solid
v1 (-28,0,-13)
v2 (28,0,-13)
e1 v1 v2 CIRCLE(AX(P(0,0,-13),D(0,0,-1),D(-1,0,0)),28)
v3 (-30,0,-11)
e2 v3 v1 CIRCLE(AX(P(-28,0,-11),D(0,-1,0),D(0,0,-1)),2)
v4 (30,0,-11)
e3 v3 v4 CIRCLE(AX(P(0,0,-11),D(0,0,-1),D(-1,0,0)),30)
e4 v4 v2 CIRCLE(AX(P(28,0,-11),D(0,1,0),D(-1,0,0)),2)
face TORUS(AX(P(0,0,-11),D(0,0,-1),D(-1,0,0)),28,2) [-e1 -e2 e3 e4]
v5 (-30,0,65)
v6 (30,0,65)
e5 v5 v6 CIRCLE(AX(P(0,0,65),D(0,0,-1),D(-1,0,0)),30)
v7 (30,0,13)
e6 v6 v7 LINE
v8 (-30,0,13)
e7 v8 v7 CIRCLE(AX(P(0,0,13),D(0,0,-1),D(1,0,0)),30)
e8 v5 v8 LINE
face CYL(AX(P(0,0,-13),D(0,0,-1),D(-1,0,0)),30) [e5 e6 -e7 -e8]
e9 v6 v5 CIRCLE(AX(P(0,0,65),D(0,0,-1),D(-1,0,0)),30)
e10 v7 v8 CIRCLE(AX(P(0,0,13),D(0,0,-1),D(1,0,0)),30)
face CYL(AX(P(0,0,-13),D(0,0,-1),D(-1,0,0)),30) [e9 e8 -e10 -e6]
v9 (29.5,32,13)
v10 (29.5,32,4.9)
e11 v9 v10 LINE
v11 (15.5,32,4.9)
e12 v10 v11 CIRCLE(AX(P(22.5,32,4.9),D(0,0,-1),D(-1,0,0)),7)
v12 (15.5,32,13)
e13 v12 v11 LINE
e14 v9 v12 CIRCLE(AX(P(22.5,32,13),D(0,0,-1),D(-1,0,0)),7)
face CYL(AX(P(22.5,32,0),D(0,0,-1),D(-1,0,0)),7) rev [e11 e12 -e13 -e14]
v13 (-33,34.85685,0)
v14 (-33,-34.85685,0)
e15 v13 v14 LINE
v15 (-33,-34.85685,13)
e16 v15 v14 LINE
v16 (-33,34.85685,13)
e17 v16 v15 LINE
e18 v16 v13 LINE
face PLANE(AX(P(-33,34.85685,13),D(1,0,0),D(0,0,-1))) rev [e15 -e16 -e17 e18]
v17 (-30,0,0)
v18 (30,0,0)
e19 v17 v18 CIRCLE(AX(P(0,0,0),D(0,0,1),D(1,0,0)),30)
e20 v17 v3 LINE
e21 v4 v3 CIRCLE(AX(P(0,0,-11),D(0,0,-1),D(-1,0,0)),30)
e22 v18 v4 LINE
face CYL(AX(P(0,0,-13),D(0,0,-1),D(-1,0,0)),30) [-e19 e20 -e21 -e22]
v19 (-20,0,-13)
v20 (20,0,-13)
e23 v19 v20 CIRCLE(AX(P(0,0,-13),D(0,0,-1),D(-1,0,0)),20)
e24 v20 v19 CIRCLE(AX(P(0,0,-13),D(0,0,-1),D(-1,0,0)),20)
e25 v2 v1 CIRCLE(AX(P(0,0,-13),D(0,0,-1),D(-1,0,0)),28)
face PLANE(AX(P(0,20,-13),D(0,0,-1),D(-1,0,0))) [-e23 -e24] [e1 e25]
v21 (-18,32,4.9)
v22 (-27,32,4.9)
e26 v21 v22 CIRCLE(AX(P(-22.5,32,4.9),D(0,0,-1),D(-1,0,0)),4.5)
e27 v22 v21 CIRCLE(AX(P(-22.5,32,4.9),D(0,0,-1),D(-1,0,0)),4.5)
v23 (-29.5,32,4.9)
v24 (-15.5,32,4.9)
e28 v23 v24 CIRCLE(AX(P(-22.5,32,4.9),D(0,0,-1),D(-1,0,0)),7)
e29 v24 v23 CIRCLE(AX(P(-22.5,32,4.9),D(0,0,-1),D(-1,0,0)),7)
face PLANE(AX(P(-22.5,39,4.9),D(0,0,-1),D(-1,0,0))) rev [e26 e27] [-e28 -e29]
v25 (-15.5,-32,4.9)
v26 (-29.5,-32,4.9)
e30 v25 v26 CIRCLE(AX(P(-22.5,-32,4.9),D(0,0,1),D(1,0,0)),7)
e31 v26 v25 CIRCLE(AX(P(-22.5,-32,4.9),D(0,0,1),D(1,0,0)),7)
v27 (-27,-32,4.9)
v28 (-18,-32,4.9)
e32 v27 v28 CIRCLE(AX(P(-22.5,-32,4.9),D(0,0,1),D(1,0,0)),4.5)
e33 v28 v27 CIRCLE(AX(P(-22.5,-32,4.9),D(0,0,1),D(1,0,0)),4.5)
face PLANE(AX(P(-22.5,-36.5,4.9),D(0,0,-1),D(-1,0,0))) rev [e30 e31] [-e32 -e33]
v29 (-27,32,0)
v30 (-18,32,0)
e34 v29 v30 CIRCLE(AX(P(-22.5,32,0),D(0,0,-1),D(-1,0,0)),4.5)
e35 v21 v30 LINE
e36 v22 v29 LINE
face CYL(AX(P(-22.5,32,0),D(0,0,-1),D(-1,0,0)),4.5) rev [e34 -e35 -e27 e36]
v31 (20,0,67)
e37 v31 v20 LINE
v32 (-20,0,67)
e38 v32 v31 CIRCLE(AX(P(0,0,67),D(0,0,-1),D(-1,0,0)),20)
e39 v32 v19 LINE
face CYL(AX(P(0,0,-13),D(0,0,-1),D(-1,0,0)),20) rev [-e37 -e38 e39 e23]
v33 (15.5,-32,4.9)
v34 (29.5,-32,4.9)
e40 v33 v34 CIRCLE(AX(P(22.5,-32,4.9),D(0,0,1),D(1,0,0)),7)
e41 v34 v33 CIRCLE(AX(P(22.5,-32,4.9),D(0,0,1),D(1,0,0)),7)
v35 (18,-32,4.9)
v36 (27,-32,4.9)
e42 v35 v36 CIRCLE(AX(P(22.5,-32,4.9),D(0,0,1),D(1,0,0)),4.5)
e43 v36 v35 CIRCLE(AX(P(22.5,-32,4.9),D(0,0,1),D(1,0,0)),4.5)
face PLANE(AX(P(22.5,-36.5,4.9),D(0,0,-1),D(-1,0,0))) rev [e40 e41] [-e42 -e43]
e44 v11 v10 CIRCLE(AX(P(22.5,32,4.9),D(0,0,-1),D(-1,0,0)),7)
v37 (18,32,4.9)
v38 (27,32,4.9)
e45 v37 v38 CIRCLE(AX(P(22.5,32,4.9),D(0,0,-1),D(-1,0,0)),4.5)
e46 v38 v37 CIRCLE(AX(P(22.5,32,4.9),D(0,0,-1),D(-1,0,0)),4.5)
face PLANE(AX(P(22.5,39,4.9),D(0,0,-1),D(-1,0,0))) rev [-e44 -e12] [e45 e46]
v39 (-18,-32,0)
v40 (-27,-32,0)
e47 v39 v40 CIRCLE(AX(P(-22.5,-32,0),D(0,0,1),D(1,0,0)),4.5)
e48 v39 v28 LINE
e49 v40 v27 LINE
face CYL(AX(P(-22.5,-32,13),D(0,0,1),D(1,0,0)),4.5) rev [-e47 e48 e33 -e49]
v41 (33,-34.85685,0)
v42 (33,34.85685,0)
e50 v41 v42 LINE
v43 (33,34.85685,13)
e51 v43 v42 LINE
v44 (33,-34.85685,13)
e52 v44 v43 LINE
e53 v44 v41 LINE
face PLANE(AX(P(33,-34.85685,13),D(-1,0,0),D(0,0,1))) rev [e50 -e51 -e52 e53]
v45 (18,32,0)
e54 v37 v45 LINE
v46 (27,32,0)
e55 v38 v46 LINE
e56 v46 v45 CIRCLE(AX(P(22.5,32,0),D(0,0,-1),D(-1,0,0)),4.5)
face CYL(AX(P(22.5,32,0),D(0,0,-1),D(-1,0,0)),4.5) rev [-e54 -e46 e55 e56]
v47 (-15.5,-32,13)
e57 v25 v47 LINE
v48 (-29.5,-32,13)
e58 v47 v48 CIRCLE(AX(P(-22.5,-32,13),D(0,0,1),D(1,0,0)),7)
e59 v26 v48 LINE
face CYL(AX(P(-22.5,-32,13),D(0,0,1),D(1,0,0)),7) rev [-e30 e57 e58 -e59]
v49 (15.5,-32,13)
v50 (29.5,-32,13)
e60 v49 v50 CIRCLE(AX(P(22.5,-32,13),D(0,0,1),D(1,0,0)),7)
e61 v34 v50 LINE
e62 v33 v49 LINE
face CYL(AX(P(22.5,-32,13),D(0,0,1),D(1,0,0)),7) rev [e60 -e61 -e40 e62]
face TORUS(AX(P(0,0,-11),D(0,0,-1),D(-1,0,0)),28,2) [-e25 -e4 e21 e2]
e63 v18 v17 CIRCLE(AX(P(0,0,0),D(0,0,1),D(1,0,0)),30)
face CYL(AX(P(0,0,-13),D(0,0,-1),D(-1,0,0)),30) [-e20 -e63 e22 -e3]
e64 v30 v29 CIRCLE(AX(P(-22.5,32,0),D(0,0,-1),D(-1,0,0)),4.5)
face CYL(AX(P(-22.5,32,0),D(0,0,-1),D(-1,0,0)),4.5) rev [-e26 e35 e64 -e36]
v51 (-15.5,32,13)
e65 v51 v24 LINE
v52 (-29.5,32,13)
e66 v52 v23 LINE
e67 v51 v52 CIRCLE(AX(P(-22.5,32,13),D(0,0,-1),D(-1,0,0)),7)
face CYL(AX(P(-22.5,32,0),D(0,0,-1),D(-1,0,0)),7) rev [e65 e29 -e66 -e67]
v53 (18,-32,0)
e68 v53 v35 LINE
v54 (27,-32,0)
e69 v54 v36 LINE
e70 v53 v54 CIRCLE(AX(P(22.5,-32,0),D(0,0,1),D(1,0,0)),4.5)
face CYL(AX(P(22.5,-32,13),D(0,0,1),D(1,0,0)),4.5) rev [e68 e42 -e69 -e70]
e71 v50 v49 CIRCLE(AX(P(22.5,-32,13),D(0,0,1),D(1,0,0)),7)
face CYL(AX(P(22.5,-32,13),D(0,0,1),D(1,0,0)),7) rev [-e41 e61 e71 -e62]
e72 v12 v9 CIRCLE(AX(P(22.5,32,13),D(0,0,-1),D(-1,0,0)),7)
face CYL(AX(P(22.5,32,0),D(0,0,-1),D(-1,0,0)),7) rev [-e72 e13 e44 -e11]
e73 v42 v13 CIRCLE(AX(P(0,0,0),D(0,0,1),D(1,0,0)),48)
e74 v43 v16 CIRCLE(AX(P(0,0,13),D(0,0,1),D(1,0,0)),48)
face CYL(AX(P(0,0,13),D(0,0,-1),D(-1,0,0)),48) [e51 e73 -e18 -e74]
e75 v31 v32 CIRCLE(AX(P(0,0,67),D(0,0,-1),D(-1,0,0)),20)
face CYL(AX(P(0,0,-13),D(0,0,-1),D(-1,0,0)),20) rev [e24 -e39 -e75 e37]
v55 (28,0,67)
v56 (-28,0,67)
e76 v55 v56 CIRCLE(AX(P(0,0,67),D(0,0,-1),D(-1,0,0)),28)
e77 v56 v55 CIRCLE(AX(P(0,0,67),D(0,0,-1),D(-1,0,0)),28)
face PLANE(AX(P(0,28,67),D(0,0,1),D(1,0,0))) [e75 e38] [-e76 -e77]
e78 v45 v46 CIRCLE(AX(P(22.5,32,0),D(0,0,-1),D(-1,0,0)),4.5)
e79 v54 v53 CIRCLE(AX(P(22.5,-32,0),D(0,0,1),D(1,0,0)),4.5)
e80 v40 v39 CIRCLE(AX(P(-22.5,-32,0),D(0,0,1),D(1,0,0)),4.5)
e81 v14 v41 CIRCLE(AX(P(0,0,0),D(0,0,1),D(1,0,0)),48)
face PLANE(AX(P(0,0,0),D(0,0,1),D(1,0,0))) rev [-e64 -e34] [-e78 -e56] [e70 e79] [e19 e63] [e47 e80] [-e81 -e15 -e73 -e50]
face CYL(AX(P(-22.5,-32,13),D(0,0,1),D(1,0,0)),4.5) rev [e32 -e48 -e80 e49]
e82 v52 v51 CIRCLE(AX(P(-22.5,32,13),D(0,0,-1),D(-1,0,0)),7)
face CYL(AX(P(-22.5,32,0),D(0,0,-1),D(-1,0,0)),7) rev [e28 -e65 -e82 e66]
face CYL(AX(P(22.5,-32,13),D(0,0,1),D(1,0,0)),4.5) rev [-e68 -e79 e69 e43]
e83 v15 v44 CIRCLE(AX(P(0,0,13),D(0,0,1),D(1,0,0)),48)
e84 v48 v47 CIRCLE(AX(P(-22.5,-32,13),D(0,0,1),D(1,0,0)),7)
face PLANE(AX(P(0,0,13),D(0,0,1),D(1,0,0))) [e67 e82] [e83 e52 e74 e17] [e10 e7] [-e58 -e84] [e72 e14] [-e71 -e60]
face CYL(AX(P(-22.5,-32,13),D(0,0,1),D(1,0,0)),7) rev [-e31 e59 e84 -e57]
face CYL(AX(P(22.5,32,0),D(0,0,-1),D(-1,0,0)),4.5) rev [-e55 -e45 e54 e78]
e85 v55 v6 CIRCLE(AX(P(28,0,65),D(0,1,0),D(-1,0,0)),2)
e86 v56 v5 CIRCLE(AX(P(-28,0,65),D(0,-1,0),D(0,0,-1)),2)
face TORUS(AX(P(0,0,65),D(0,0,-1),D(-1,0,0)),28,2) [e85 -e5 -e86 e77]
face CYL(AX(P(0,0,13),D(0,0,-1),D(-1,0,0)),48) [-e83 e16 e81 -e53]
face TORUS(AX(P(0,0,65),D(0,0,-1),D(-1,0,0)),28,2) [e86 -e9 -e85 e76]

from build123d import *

# Parameters (mm, degrees)
EXTRUDE_START   = 13
SKETCH_2_R      = 30
EXTRUDE_1_DEPTH = 13


with BuildPart() as part:
    # 草图1 → 旋转1 (revolve)
    with BuildSketch(Plane(origin=(0, 0, 0), x_dir=(0, 0, -1), z_dir=(1, 0, 0)), mode=Mode.PRIVATE) as revolve_1_sk:
        with BuildLine():
            Line((-67, 28), (-67, 20))
            Line((-67, 20), (13, 20))
            Line((13, 20), (13, 28))
            ThreePointArc((13, 28), (12.414213562, 29.414213562), (11, 30))
            Line((11, 30), (-65, 30))
            ThreePointArc((-65, 30), (-66.414213562, 29.414213562), (-67, 28))
        make_face()
    revolve(revolve_1_sk.sketch.rotate(Axis((0, 0, -13), (0, 0, 1)), 90), axis=Axis((0, 0, -13), (0, 0, 1)))

    # 草图2 → 凸台-拉伸1 (add)
    with BuildSketch(Plane.XY.offset(EXTRUDE_START)):
        with BuildLine():
            Line((-33, 34.856850116), (-33, -34.856850116))
            ThreePointArc((-33, -34.856850116), (0, -48), (33, -34.856850116))
            Line((33, -34.856850116), (33, 34.856850116))
            ThreePointArc((33, 34.856850116), (0, 48), (-33, 34.856850116))
        make_face()
        with Locations(Location((0, 0, 0), (0, 0, 180))):
            Circle(SKETCH_2_R, mode=Mode.SUBTRACT)
    extrude(amount=-EXTRUDE_1_DEPTH)

    # 草图3 → 切除-旋转1 (revolve, cut)
    with BuildSketch(Plane(origin=(-22.5, 0, 0), x_dir=(0, 0, -1), z_dir=(1, 0, 0)), mode=Mode.PRIVATE) as cut_revolve_1_sk:
        Polygon((-13, 32), (-13, 39), (-4.9, 39), (-4.9, 36.5), (0, 36.5), (0, 32), align=None)
    revolve(cut_revolve_1_sk.sketch.rotate(Axis((-22.5, 32, 0), (0, 0, 1)), 90), axis=Axis((-22.5, 32, 0), (0, 0, 1)), mode=Mode.SUBTRACT)

    # 草图4 → 切除-旋转2 (revolve, cut)
    with BuildSketch(Plane(origin=(-22.5, 0, 0), x_dir=(0, 0, -1), z_dir=(1, 0, 0)), mode=Mode.PRIVATE) as cut_revolve_2_sk:
        Polygon((0, -32), (0, -36.5), (-4.9, -36.5), (-4.9, -39), (-13, -39), (-13, -32), align=None)
    revolve(cut_revolve_2_sk.sketch.rotate(Axis((-22.5, -32, 13), (0, 0, -1)), 270), axis=Axis((-22.5, -32, 13), (0, 0, -1)), mode=Mode.SUBTRACT)

    # 草图5 → 切除-旋转3 (revolve, cut)
    with BuildSketch(Plane(origin=(22.5, 0, 0), x_dir=(0, 0, -1), z_dir=(1, 0, 0)), mode=Mode.PRIVATE) as cut_revolve_3_sk:
        Polygon((-13, 32), (-13, 39), (-4.9, 39), (-4.9, 36.5), (0, 36.5), (0, 32), align=None)
    revolve(cut_revolve_3_sk.sketch.rotate(Axis((22.5, 32, 0), (0, 0, 1)), 90), axis=Axis((22.5, 32, 0), (0, 0, 1)), mode=Mode.SUBTRACT)

    # 草图6 → 切除-旋转4 (revolve, cut)
    with BuildSketch(Plane(origin=(22.5, 0, 0), x_dir=(0, 0, -1), z_dir=(1, 0, 0)), mode=Mode.PRIVATE) as cut_revolve_4_sk:
        Polygon((0, -32), (0, -36.5), (-4.9, -36.5), (-4.9, -39), (-13, -39), (-13, -32), align=None)
    revolve(cut_revolve_4_sk.sketch.rotate(Axis((22.5, -32, 13), (0, 0, -1)), 270), axis=Axis((22.5, -32, 13), (0, 0, -1)), mode=Mode.SUBTRACT)


solid = part.part
